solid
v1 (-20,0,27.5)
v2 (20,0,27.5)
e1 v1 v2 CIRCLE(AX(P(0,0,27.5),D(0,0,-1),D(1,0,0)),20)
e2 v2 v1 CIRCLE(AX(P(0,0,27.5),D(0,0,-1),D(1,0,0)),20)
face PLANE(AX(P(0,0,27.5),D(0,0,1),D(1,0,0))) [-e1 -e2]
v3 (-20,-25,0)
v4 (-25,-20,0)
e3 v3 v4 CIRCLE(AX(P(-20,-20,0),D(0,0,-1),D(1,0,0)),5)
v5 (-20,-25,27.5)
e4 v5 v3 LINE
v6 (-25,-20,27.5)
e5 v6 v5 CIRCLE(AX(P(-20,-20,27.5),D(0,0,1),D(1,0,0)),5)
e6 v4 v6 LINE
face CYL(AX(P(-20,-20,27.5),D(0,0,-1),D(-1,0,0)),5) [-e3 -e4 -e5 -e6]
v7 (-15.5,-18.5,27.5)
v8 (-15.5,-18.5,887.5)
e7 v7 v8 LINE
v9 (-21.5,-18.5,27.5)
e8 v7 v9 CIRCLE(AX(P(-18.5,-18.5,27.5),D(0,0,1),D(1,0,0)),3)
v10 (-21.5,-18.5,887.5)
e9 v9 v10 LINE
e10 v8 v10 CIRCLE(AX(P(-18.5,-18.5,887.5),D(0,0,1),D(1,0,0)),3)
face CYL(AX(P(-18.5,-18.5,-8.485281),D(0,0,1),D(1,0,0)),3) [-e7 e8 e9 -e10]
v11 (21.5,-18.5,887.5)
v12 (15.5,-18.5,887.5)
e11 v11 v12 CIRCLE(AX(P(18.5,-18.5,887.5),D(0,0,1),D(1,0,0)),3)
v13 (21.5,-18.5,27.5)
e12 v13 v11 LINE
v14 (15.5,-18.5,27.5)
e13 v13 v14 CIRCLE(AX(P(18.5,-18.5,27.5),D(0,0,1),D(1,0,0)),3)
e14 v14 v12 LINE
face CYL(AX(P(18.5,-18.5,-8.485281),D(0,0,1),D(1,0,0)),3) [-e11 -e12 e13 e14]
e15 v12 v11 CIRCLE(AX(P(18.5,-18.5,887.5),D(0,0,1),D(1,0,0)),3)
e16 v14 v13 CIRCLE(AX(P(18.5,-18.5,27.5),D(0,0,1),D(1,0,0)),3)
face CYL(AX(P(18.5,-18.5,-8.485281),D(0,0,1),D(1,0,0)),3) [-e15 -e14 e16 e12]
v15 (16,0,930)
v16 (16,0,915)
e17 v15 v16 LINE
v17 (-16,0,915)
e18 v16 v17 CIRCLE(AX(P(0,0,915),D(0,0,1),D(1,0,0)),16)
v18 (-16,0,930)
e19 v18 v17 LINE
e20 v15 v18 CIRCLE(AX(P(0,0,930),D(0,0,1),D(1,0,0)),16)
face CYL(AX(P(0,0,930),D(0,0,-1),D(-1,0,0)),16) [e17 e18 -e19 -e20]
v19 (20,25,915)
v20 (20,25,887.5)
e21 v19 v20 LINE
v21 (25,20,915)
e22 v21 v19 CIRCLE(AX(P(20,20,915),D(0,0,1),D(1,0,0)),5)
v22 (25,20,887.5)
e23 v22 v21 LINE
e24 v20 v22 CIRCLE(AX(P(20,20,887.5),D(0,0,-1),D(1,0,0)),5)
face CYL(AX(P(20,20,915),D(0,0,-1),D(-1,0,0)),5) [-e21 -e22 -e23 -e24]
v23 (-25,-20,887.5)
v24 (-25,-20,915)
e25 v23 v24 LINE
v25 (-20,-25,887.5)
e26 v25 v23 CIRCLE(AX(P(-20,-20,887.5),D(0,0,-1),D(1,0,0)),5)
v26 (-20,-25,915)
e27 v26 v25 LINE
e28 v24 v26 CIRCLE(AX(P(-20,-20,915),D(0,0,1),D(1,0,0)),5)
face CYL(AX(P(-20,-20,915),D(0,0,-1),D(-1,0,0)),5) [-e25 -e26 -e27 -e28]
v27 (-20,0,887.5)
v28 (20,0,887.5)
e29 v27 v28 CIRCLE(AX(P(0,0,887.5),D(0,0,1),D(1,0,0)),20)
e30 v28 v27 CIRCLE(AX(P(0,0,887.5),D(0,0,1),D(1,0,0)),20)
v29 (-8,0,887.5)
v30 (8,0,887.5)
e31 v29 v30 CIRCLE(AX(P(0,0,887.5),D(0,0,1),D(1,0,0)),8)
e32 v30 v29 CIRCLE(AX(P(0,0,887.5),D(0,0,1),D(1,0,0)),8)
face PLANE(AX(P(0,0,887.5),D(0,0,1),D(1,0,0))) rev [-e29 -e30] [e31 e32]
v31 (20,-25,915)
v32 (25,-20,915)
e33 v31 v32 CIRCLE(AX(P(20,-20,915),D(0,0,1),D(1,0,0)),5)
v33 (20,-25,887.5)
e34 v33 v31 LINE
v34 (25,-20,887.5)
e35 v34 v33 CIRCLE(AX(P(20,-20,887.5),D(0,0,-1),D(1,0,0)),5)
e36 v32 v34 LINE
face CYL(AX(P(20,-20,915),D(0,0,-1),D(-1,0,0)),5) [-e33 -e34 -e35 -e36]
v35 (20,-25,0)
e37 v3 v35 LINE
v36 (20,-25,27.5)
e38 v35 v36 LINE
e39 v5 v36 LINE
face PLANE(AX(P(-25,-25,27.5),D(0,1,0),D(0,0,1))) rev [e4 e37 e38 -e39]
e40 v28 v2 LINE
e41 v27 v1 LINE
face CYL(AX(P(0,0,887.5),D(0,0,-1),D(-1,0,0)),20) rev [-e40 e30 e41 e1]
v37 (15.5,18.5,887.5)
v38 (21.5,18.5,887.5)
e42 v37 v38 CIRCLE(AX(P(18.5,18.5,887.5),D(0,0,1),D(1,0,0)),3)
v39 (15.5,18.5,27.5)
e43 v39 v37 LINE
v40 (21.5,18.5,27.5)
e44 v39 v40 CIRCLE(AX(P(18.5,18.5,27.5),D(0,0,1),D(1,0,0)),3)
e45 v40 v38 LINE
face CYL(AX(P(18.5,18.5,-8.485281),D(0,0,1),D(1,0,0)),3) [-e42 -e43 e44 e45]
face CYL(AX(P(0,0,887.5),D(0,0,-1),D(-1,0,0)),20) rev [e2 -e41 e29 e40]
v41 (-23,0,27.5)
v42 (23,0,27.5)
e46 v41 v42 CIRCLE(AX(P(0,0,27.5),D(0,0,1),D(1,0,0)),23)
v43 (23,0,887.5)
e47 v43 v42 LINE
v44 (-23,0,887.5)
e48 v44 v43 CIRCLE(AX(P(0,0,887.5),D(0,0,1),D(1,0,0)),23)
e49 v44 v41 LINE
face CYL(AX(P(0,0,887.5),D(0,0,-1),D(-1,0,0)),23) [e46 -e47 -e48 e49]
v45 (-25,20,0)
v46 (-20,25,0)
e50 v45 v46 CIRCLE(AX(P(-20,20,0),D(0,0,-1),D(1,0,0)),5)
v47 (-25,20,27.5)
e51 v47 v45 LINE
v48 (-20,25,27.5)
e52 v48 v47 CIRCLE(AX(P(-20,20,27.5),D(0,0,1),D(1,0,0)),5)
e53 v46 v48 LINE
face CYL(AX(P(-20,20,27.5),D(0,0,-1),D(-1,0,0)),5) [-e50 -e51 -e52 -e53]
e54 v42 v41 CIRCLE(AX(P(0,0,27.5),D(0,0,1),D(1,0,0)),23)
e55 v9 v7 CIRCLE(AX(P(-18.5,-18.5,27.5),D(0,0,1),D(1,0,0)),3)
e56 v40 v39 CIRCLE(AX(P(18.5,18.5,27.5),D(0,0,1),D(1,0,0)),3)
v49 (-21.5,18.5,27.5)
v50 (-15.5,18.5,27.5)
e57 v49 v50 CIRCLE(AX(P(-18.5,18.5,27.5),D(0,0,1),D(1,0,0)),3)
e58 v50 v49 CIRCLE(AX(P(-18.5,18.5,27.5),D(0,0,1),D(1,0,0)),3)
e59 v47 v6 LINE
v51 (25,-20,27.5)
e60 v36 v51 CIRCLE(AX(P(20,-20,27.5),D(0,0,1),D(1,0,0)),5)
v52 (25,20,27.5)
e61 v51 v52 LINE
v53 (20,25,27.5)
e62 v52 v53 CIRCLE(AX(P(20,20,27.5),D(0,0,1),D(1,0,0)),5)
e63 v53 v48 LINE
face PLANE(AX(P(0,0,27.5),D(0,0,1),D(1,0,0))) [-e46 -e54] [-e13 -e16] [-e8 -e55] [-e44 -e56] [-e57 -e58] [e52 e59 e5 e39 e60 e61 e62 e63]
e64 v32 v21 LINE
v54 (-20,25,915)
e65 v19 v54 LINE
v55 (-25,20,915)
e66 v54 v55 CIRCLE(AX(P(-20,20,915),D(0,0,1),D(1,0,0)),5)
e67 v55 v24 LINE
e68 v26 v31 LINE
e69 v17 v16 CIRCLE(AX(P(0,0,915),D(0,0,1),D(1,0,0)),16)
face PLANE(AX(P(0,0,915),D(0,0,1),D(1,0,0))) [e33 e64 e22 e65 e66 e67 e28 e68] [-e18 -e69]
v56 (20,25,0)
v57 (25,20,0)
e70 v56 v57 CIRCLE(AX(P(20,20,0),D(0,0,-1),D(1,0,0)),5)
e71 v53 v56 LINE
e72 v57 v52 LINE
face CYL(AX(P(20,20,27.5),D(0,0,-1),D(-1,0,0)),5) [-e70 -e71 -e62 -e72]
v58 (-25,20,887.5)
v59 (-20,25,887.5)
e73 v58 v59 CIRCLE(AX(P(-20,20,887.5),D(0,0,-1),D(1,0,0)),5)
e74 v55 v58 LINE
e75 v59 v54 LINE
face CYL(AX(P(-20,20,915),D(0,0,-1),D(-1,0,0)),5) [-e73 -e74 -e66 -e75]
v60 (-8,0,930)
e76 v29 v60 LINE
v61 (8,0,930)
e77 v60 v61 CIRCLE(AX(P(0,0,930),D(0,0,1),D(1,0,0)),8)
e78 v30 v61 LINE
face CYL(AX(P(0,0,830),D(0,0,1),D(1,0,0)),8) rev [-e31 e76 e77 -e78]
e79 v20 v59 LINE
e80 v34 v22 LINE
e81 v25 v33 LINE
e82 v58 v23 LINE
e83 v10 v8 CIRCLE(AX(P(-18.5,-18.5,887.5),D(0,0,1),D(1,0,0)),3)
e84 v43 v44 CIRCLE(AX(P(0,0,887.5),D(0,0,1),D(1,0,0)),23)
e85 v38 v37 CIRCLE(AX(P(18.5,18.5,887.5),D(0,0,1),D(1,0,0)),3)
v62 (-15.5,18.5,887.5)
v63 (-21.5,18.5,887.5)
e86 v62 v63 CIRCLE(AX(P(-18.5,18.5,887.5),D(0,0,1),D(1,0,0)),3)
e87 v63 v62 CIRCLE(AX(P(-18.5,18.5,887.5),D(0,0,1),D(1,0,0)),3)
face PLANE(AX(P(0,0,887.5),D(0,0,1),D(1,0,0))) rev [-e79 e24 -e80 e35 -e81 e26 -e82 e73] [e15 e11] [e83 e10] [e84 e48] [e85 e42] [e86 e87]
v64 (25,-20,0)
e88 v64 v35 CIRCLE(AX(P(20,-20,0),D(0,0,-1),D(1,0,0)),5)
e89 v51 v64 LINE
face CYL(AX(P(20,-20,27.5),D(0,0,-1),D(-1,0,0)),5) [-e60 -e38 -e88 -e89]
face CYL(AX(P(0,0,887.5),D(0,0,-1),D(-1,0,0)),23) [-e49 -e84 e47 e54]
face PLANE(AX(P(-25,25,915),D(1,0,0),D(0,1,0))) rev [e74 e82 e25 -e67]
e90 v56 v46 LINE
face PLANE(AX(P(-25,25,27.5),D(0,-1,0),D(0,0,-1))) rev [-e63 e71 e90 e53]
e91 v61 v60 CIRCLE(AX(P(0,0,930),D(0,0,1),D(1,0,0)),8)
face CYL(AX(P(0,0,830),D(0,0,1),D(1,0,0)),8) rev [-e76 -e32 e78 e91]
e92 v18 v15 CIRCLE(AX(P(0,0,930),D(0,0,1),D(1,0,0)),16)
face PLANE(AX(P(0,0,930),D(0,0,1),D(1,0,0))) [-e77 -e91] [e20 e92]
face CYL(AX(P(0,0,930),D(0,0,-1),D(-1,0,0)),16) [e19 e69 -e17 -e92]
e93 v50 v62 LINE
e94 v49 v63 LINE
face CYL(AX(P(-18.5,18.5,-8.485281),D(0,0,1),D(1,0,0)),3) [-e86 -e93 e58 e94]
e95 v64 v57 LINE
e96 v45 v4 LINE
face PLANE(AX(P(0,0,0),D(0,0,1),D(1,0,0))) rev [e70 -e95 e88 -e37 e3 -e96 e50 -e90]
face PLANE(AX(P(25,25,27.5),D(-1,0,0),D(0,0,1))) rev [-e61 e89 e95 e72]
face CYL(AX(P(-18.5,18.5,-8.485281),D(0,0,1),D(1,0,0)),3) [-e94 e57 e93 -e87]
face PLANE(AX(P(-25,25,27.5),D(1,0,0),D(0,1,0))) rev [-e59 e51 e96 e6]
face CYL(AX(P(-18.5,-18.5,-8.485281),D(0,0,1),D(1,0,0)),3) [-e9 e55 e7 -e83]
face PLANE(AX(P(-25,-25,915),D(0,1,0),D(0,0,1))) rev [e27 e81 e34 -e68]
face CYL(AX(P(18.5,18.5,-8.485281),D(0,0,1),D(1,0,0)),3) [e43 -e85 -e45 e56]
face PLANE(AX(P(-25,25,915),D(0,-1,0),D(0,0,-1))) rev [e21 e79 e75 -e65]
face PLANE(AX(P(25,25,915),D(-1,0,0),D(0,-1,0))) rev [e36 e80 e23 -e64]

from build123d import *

# Parameters (mm, degrees)
SKETCH1_W           = 50
SKETCH1_H           = 50
BOSS_EXTRUDE1_DEPTH = 27.5
SKETCH2_R           = 23
SKETCH2_R_2         = 20
BOSS_EXTRUDE2_DEPTH = 860
SKETCH3_W           = 50
SKETCH3_H           = 50
BOSS_EXTRUDE3_DEPTH = 27.5
SKETCH4_R           = 16
BOSS_EXTRUDE4_DEPTH = 15
SKETCH5_R           = 8
CUT_EXTRUDE1_DEPTH  = 100
SKETCH6_R           = 3
BOSS_EXTRUDE5_DEPTH = 915
FILLET1_R           = 5


with BuildPart() as part:
    # Sketch1 → Boss-Extrude1 (new body)
    with BuildSketch(Plane.XY):
        Rectangle(SKETCH1_W, SKETCH1_H)
    extrude(amount=BOSS_EXTRUDE1_DEPTH)

    # Sketch2 → Boss-Extrude2 (add)
    with BuildSketch(Plane.XY.offset(27.5)):
        Circle(SKETCH2_R)
        Circle(SKETCH2_R_2, mode=Mode.SUBTRACT)
    extrude(amount=BOSS_EXTRUDE2_DEPTH)

    # Sketch3 → Boss-Extrude3 (add)
    with BuildSketch(Plane.XY.offset(887.5)):
        Rectangle(SKETCH3_W, SKETCH3_H)
    extrude(amount=BOSS_EXTRUDE3_DEPTH)

    # Sketch4 → Boss-Extrude4 (add)
    with BuildSketch(Plane.XY.offset(915)):
        Circle(SKETCH4_R)
    extrude(amount=BOSS_EXTRUDE4_DEPTH)

    # Sketch5 → Cut-Extrude1 (cut)
    with BuildSketch(Plane.XY.offset(930)):
        Circle(SKETCH5_R)
    extrude(amount=-CUT_EXTRUDE1_DEPTH, mode=Mode.SUBTRACT)

    # Sketch6 → Boss-Extrude5 (add)
    with BuildSketch(Plane.XY.offset(915)):
        with Locations((-18.5, 18.5)):
            Circle(SKETCH6_R)
        with Locations((18.5, 18.5)):
            Circle(SKETCH6_R)
        with Locations((18.5, -18.5)):
            Circle(SKETCH6_R)
        with Locations((-18.5, -18.5)):
            Circle(SKETCH6_R)
    extrude(amount=-BOSS_EXTRUDE5_DEPTH)

    # Fillet1
    fillet1_edges = [part.edges().sort_by_distance(p)[0] for p in [
        (25, -25, 901.25),
        (25, 25, 901.25),
        (-25, 25, 901.25),
        (-25, -25, 901.25),
        (25, -25, 13.75),
        (-25, -25, 13.75),
        (-25, 25, 13.75),
        (25, 25, 13.75),
    ]]
    fillet(fillet1_edges, radius=FILLET1_R)


solid = part.part
